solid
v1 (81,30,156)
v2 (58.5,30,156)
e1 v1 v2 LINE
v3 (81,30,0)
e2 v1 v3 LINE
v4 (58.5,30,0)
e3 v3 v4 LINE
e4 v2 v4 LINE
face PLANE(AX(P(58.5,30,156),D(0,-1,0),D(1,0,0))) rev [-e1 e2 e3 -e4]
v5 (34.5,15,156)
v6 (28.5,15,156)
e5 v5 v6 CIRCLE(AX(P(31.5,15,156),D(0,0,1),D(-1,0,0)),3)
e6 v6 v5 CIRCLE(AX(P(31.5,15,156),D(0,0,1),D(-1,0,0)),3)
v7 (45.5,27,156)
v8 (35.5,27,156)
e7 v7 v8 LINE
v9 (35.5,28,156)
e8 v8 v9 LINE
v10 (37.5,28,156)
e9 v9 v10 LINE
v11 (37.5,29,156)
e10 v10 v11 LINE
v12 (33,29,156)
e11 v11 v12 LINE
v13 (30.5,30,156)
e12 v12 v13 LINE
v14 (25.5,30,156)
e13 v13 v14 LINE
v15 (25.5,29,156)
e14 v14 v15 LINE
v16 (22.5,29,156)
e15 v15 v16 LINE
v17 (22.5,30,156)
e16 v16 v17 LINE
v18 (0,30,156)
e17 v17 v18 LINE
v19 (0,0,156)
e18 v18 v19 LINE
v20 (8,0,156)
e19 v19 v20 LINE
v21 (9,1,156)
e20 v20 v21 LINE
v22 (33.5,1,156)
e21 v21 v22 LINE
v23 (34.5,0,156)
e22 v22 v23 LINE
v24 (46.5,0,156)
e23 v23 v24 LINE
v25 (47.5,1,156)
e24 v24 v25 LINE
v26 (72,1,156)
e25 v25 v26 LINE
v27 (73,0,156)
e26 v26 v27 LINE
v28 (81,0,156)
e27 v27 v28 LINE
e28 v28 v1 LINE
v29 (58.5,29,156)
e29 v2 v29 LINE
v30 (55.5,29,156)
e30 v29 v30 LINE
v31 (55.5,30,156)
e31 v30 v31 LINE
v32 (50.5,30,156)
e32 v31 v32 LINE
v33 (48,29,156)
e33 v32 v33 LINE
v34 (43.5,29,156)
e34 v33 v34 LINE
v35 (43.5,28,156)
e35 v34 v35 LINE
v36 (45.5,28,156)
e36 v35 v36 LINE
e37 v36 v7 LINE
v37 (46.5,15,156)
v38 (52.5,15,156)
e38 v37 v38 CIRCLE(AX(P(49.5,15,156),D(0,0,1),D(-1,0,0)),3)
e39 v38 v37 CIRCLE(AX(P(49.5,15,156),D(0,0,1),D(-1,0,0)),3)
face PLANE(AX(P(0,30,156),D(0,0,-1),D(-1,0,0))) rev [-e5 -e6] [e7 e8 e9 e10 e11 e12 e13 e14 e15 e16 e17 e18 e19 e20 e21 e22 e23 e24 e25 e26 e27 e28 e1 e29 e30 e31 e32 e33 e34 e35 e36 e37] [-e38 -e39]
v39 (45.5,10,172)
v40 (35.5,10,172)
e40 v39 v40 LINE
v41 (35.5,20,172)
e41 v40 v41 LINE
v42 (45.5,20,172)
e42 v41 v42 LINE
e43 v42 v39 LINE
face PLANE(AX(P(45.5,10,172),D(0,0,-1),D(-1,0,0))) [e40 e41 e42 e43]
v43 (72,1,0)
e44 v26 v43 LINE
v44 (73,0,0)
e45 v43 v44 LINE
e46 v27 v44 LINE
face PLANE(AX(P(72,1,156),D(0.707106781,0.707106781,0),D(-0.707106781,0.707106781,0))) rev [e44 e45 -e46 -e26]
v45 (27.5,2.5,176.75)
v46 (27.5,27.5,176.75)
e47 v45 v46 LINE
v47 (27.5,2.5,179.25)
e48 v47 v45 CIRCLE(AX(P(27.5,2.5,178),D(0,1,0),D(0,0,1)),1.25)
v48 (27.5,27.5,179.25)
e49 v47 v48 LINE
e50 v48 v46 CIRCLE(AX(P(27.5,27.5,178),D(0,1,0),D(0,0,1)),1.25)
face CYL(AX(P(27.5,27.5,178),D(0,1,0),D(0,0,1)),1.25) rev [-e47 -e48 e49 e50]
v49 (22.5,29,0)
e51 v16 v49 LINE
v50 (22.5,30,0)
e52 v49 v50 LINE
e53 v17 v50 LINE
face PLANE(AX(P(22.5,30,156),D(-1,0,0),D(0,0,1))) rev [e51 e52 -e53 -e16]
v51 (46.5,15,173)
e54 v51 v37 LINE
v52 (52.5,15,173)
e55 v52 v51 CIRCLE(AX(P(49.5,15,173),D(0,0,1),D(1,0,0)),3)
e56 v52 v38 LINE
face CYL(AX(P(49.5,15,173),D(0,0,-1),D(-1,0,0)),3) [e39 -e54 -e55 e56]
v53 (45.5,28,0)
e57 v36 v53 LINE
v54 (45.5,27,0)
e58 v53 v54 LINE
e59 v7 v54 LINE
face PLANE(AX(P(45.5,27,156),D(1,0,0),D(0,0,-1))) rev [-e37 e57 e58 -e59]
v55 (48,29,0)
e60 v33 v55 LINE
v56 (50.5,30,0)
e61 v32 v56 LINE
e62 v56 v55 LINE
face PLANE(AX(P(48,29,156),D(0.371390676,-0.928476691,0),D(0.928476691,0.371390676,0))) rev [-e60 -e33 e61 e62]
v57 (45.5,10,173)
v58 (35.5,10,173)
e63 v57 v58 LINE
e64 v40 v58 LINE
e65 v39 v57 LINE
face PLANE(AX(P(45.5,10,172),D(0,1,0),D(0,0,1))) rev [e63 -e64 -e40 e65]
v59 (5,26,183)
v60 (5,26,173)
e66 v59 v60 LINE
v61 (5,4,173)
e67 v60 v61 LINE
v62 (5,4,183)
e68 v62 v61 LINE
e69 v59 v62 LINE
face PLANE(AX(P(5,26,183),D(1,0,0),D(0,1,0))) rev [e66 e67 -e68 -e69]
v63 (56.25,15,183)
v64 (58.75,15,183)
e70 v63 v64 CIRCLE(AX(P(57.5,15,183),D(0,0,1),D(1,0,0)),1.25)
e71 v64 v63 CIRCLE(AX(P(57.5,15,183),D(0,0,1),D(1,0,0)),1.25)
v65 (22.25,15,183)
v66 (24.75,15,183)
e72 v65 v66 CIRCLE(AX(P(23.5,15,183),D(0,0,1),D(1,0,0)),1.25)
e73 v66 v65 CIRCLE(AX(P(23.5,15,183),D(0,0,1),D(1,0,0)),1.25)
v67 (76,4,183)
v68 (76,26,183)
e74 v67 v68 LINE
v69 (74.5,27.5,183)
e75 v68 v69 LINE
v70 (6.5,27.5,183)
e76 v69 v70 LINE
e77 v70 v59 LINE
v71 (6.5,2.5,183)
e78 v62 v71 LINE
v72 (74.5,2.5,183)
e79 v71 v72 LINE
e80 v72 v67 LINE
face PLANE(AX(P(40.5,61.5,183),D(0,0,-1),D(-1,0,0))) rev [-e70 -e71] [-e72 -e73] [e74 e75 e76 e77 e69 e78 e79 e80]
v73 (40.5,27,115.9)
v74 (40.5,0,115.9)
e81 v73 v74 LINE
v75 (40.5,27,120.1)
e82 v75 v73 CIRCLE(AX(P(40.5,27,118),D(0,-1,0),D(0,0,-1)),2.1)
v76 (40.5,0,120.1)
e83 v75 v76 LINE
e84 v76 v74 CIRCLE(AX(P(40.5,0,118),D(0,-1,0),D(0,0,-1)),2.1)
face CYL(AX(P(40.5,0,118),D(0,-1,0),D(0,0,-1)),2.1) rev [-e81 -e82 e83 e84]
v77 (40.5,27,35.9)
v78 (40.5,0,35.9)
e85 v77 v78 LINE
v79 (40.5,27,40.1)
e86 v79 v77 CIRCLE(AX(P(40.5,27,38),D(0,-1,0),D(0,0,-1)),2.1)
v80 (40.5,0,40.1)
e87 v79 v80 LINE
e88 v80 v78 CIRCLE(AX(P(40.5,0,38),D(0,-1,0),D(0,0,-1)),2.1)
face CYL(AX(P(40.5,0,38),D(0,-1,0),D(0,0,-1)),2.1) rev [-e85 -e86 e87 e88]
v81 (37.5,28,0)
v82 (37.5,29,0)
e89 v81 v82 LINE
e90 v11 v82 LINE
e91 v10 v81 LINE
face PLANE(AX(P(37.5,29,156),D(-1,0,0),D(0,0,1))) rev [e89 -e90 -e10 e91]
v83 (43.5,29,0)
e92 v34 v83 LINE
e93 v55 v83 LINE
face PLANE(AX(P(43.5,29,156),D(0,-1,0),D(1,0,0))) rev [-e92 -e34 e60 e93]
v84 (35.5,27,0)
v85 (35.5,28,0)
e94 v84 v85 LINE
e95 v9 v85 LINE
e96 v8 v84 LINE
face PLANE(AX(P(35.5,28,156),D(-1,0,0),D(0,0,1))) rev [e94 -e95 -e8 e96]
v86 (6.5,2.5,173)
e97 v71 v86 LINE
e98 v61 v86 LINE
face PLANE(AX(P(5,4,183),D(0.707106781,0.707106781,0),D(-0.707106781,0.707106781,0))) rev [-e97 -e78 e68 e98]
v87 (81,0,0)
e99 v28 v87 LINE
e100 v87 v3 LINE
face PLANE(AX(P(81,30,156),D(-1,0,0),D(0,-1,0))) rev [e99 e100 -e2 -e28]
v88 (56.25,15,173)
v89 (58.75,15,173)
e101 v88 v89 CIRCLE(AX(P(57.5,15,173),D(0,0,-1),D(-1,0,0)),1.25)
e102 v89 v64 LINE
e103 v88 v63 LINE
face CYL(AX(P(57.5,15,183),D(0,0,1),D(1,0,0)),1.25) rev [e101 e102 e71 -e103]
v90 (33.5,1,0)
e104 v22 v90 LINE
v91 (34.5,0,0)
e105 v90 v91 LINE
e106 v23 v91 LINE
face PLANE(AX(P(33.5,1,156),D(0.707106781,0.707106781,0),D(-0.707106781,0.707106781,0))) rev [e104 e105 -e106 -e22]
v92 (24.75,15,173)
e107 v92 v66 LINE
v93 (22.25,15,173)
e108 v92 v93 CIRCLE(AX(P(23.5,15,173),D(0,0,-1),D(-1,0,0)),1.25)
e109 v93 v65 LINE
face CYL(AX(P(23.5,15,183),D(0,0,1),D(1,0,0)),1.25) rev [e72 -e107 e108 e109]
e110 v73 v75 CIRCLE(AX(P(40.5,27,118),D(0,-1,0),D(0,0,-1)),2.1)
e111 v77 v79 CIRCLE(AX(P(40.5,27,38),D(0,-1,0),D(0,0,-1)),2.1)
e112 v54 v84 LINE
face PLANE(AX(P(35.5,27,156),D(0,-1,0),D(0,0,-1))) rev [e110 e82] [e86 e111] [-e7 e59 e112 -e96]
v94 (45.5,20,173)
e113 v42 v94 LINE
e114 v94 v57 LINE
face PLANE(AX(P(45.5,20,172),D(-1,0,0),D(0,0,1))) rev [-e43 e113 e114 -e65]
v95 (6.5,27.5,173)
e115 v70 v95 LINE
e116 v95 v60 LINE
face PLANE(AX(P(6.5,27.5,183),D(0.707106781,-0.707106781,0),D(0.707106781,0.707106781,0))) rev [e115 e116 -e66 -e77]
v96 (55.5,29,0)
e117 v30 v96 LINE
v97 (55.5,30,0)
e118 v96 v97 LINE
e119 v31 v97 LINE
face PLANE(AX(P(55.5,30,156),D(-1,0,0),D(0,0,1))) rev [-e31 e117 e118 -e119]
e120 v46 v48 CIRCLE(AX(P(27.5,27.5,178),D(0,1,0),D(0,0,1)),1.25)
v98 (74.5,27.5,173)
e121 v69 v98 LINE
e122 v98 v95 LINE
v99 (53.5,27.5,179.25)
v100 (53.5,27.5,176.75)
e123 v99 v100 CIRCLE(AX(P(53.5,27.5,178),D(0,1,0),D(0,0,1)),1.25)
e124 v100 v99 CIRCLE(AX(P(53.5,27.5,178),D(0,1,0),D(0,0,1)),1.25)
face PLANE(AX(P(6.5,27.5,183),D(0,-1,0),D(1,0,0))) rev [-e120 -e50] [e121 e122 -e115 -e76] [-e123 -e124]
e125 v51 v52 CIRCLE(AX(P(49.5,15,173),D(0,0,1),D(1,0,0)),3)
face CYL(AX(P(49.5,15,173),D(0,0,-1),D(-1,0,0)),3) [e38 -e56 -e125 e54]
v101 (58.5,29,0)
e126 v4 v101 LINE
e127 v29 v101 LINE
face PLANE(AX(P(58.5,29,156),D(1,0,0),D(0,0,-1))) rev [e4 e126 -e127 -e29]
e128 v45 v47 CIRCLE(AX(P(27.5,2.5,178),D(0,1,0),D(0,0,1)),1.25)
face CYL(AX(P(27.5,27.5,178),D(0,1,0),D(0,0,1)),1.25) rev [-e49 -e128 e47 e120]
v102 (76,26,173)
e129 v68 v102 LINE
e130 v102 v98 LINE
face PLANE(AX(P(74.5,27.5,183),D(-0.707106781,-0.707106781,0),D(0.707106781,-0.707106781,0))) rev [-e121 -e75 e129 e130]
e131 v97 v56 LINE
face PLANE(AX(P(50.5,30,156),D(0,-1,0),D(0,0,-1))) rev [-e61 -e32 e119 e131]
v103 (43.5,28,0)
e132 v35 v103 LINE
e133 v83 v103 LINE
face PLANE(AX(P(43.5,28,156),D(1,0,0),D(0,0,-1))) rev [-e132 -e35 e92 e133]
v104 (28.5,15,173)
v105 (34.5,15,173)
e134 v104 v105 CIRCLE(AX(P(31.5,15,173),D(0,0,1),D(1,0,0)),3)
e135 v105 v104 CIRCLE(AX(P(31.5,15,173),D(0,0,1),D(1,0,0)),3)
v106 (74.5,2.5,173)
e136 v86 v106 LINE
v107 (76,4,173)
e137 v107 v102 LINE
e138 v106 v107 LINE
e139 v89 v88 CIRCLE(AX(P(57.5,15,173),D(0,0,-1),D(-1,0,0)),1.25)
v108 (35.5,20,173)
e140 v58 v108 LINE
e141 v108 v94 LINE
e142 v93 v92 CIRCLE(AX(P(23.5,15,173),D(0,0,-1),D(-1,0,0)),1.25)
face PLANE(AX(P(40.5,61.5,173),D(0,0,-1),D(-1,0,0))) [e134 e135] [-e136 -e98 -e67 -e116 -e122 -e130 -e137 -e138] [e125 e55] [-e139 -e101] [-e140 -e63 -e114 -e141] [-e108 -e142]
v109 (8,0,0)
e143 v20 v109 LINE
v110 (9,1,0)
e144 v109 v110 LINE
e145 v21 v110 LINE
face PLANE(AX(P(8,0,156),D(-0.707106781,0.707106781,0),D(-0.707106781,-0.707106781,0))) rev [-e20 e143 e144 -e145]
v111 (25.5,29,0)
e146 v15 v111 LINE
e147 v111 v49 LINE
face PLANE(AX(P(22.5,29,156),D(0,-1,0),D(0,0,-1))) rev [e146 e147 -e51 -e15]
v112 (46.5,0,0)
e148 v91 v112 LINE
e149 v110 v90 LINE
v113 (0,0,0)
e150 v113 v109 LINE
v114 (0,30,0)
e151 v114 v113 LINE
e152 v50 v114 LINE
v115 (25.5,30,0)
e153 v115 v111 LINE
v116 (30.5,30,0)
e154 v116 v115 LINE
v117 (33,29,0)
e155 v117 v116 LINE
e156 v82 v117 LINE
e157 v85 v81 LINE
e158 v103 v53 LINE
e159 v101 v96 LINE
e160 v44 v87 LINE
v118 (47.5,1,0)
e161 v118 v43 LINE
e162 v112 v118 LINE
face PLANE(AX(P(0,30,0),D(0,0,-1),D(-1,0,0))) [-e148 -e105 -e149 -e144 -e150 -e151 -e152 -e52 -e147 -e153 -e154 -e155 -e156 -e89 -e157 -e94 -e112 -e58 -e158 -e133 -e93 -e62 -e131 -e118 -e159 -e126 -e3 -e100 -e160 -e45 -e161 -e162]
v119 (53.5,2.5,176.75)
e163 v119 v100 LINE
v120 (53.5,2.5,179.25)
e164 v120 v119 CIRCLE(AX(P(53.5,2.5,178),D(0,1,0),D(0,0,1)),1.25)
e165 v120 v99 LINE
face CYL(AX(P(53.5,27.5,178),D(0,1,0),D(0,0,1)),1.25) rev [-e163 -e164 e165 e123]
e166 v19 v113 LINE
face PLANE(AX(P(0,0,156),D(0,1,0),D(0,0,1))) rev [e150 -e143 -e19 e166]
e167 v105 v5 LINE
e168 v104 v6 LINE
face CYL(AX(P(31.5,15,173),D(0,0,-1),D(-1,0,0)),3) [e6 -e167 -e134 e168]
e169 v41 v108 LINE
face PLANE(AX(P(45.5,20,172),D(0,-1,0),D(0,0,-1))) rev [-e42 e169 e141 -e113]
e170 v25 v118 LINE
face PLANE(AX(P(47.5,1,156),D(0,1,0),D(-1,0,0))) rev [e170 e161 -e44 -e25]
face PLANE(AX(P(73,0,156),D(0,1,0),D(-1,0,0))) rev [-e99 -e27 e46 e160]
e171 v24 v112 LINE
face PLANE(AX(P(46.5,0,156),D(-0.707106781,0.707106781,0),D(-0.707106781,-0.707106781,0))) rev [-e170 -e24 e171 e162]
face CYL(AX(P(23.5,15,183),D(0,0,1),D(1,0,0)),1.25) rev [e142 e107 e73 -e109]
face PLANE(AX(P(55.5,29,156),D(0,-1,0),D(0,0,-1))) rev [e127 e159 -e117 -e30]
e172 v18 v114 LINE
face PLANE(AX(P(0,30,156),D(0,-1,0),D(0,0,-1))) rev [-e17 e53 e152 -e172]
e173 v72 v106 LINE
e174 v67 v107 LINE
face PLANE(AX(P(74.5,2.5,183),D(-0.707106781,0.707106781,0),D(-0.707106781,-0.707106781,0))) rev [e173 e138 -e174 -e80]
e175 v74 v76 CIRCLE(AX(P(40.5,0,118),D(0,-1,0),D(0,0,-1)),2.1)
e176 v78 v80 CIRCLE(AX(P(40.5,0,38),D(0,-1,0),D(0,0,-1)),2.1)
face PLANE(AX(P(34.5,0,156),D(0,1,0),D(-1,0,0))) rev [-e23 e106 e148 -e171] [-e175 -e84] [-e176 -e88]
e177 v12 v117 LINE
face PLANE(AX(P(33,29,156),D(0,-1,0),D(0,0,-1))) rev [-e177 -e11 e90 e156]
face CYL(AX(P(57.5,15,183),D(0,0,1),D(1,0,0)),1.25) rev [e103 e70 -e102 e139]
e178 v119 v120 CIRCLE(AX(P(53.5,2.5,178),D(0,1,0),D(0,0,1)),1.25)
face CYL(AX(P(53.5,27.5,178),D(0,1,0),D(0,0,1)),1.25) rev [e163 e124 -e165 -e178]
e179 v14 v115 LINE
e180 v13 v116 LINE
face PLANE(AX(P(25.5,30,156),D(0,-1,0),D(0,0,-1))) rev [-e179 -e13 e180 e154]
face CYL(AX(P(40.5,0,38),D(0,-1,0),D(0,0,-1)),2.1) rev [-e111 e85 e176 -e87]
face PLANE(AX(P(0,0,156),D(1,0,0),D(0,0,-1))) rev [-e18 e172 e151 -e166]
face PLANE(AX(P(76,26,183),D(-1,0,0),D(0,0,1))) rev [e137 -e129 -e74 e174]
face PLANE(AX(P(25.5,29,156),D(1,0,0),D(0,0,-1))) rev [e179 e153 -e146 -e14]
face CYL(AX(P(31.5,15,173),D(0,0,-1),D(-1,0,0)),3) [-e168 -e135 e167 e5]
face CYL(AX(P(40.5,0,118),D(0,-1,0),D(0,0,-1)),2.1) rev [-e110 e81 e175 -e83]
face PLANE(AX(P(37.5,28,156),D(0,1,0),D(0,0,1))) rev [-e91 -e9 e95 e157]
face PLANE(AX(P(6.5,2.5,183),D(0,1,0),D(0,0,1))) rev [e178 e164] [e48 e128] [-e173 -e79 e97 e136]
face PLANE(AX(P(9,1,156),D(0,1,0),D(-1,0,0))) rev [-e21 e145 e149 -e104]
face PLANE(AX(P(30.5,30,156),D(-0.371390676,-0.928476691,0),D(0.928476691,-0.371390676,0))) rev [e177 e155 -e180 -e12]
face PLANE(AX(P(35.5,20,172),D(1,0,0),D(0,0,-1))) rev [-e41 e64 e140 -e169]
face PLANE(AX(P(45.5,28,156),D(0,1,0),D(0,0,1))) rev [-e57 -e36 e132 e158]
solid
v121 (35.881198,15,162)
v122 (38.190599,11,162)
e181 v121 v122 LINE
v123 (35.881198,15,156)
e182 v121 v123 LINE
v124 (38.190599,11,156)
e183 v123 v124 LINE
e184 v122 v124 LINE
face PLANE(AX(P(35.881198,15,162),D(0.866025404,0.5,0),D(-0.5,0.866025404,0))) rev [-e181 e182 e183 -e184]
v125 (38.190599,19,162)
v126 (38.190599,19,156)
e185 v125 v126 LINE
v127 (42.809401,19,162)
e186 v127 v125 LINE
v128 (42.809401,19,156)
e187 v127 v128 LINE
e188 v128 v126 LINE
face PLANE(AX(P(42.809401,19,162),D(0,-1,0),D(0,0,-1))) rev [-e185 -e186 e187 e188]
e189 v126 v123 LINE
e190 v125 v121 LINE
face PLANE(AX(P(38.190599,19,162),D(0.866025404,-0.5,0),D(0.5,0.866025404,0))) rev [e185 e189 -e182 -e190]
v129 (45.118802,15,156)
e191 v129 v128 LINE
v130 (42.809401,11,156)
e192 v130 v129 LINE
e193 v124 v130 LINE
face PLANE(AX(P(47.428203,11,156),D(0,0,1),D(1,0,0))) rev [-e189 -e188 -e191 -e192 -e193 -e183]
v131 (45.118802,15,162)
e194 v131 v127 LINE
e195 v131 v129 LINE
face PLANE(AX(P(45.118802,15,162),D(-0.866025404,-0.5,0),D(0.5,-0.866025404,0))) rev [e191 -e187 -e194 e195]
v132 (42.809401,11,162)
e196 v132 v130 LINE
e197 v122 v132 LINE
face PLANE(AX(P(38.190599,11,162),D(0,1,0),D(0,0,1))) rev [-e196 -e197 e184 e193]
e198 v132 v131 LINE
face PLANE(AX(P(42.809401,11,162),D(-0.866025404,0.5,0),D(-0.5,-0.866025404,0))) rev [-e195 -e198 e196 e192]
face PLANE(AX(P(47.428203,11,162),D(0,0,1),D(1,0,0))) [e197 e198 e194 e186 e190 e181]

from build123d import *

# Parameters (mm, degrees)
EXTRUDE1_DEPTH             = 156
SKETCH2_R                  = 3
EXTRUDE2_DEPTH             = 17
EXTRUDE3_DEPTH             = 10
M3X0_5_TAPPED_HOLE1_D      = 2.5
M3X0_5_TAPPED_HOLE1_DEPTH  = 10
M3X0_5_TAPPED_HOLE2_D      = 2.5
SKETCH15_W                 = 10
SKETCH15_H                 = 10
EXTRUDE4_DEPTH             = 1
EXTRUDE5_DEPTH             = 6
SKETCH20_W                 = 2.1
SKETCH20_H                 = 30
M5_TAPPED_HOLE1_AT_2_COUNT = 2
M5_TAPPED_HOLE1_AT_2_PITCH = 80


with BuildPart() as part:
    # Sketch1 → Extrude1 (new body)
    with BuildSketch(Plane.XY):
        Polygon((0, 0), (8, 0), (9, 1), (33.5, 1), (34.5, 0), (46.5, 0), (47.5, 1), (72, 1), (73, 0), (81, 0), (81, 30), (58.5, 30), (58.5, 29), (55.5, 29), (55.5, 30), (50.5, 30), (48, 29), (43.5, 29), (43.5, 28), (45.5, 28), (45.5, 27), (35.5, 27), (35.5, 28), (37.5, 28), (37.5, 29), (33, 29), (30.5, 30), (25.5, 30), (25.5, 29), (22.5, 29), (22.5, 30), (0, 30), align=None)
    extrude(amount=EXTRUDE1_DEPTH)

    # Sketch2 → Extrude2 (add)
    with BuildSketch(Plane.XY.offset(156)):
        with Locations(Location((31.5, 15, 0), (0, 0, 180))):
            Circle(SKETCH2_R)
        with Locations(Location((49.5, 15, 0), (0, 0, 180))):
            Circle(SKETCH2_R)
    extrude(amount=EXTRUDE2_DEPTH)

    # Sketch3 → Extrude3 (add)
    with BuildSketch(Plane.XY.offset(173)):
        Polygon((6.5, 27.5), (74.5, 27.5), (76, 26), (76, 4), (74.5, 2.5), (6.5, 2.5), (5, 4), (5, 26), align=None)
    extrude(amount=EXTRUDE3_DEPTH)

    # M3x0.5 Tapped Hole1
    with Locations(Plane.XY.offset(183)):
        with Locations((23.5, 15), (57.5, 15)):
            Hole(M3X0_5_TAPPED_HOLE1_D / 2, depth=M3X0_5_TAPPED_HOLE1_DEPTH)

    # M3x0.5 Tapped Hole2 (through all)
    with Locations(Plane(origin=(0, 27.5, 0), x_dir=(-1, 0, 0), z_dir=(0, 1, 0))):
        with Locations((-27.5, 178), (-53.5, 178)):
            Hole(M3X0_5_TAPPED_HOLE2_D / 2)

    # Sketch15 → Extrude4 (add)
    with BuildSketch(Plane(origin=(0, 0, 173), x_dir=(-1, 0, 0), z_dir=(0, 0, -1))):
        with Locations((-40.5, 15)):
            Rectangle(SKETCH15_W, SKETCH15_H)
    extrude(amount=EXTRUDE4_DEPTH)

    # Sketch20 → M5 Tapped Hole1 (revolve, cut)
    with BuildSketch(Plane(origin=(40.5, 0, 118), x_dir=(0, 0, -1), z_dir=(1, 0, 0))):
        with Locations((1.05, 15)):
            Rectangle(SKETCH20_W, SKETCH20_H)
    m5_tapped_hole1 = revolve(axis=Axis((40.5, -6.35, 118), (0, 1, 0)), mode=Mode.SUBTRACT)

    # M5 Tapped Hole1 at 2: M5 Tapped Hole1 ×2
    with Locations(*[(0, 0, -i * M5_TAPPED_HOLE1_AT_2_PITCH) for i in range(1, M5_TAPPED_HOLE1_AT_2_COUNT)]):
        add(m5_tapped_hole1, mode=Mode.SUBTRACT)


with BuildPart() as body_2:
    # Sketch16 → Extrude5 (new body)
    with BuildSketch(Plane.XY.offset(156)):
        Polygon((42.809401077, 11), (45.118802154, 15), (42.809401077, 19), (38.190598923, 19), (35.881197846, 15), (38.190598923, 11), align=None)
    extrude(amount=EXTRUDE5_DEPTH)


solid = Compound([part.part, body_2.part])
